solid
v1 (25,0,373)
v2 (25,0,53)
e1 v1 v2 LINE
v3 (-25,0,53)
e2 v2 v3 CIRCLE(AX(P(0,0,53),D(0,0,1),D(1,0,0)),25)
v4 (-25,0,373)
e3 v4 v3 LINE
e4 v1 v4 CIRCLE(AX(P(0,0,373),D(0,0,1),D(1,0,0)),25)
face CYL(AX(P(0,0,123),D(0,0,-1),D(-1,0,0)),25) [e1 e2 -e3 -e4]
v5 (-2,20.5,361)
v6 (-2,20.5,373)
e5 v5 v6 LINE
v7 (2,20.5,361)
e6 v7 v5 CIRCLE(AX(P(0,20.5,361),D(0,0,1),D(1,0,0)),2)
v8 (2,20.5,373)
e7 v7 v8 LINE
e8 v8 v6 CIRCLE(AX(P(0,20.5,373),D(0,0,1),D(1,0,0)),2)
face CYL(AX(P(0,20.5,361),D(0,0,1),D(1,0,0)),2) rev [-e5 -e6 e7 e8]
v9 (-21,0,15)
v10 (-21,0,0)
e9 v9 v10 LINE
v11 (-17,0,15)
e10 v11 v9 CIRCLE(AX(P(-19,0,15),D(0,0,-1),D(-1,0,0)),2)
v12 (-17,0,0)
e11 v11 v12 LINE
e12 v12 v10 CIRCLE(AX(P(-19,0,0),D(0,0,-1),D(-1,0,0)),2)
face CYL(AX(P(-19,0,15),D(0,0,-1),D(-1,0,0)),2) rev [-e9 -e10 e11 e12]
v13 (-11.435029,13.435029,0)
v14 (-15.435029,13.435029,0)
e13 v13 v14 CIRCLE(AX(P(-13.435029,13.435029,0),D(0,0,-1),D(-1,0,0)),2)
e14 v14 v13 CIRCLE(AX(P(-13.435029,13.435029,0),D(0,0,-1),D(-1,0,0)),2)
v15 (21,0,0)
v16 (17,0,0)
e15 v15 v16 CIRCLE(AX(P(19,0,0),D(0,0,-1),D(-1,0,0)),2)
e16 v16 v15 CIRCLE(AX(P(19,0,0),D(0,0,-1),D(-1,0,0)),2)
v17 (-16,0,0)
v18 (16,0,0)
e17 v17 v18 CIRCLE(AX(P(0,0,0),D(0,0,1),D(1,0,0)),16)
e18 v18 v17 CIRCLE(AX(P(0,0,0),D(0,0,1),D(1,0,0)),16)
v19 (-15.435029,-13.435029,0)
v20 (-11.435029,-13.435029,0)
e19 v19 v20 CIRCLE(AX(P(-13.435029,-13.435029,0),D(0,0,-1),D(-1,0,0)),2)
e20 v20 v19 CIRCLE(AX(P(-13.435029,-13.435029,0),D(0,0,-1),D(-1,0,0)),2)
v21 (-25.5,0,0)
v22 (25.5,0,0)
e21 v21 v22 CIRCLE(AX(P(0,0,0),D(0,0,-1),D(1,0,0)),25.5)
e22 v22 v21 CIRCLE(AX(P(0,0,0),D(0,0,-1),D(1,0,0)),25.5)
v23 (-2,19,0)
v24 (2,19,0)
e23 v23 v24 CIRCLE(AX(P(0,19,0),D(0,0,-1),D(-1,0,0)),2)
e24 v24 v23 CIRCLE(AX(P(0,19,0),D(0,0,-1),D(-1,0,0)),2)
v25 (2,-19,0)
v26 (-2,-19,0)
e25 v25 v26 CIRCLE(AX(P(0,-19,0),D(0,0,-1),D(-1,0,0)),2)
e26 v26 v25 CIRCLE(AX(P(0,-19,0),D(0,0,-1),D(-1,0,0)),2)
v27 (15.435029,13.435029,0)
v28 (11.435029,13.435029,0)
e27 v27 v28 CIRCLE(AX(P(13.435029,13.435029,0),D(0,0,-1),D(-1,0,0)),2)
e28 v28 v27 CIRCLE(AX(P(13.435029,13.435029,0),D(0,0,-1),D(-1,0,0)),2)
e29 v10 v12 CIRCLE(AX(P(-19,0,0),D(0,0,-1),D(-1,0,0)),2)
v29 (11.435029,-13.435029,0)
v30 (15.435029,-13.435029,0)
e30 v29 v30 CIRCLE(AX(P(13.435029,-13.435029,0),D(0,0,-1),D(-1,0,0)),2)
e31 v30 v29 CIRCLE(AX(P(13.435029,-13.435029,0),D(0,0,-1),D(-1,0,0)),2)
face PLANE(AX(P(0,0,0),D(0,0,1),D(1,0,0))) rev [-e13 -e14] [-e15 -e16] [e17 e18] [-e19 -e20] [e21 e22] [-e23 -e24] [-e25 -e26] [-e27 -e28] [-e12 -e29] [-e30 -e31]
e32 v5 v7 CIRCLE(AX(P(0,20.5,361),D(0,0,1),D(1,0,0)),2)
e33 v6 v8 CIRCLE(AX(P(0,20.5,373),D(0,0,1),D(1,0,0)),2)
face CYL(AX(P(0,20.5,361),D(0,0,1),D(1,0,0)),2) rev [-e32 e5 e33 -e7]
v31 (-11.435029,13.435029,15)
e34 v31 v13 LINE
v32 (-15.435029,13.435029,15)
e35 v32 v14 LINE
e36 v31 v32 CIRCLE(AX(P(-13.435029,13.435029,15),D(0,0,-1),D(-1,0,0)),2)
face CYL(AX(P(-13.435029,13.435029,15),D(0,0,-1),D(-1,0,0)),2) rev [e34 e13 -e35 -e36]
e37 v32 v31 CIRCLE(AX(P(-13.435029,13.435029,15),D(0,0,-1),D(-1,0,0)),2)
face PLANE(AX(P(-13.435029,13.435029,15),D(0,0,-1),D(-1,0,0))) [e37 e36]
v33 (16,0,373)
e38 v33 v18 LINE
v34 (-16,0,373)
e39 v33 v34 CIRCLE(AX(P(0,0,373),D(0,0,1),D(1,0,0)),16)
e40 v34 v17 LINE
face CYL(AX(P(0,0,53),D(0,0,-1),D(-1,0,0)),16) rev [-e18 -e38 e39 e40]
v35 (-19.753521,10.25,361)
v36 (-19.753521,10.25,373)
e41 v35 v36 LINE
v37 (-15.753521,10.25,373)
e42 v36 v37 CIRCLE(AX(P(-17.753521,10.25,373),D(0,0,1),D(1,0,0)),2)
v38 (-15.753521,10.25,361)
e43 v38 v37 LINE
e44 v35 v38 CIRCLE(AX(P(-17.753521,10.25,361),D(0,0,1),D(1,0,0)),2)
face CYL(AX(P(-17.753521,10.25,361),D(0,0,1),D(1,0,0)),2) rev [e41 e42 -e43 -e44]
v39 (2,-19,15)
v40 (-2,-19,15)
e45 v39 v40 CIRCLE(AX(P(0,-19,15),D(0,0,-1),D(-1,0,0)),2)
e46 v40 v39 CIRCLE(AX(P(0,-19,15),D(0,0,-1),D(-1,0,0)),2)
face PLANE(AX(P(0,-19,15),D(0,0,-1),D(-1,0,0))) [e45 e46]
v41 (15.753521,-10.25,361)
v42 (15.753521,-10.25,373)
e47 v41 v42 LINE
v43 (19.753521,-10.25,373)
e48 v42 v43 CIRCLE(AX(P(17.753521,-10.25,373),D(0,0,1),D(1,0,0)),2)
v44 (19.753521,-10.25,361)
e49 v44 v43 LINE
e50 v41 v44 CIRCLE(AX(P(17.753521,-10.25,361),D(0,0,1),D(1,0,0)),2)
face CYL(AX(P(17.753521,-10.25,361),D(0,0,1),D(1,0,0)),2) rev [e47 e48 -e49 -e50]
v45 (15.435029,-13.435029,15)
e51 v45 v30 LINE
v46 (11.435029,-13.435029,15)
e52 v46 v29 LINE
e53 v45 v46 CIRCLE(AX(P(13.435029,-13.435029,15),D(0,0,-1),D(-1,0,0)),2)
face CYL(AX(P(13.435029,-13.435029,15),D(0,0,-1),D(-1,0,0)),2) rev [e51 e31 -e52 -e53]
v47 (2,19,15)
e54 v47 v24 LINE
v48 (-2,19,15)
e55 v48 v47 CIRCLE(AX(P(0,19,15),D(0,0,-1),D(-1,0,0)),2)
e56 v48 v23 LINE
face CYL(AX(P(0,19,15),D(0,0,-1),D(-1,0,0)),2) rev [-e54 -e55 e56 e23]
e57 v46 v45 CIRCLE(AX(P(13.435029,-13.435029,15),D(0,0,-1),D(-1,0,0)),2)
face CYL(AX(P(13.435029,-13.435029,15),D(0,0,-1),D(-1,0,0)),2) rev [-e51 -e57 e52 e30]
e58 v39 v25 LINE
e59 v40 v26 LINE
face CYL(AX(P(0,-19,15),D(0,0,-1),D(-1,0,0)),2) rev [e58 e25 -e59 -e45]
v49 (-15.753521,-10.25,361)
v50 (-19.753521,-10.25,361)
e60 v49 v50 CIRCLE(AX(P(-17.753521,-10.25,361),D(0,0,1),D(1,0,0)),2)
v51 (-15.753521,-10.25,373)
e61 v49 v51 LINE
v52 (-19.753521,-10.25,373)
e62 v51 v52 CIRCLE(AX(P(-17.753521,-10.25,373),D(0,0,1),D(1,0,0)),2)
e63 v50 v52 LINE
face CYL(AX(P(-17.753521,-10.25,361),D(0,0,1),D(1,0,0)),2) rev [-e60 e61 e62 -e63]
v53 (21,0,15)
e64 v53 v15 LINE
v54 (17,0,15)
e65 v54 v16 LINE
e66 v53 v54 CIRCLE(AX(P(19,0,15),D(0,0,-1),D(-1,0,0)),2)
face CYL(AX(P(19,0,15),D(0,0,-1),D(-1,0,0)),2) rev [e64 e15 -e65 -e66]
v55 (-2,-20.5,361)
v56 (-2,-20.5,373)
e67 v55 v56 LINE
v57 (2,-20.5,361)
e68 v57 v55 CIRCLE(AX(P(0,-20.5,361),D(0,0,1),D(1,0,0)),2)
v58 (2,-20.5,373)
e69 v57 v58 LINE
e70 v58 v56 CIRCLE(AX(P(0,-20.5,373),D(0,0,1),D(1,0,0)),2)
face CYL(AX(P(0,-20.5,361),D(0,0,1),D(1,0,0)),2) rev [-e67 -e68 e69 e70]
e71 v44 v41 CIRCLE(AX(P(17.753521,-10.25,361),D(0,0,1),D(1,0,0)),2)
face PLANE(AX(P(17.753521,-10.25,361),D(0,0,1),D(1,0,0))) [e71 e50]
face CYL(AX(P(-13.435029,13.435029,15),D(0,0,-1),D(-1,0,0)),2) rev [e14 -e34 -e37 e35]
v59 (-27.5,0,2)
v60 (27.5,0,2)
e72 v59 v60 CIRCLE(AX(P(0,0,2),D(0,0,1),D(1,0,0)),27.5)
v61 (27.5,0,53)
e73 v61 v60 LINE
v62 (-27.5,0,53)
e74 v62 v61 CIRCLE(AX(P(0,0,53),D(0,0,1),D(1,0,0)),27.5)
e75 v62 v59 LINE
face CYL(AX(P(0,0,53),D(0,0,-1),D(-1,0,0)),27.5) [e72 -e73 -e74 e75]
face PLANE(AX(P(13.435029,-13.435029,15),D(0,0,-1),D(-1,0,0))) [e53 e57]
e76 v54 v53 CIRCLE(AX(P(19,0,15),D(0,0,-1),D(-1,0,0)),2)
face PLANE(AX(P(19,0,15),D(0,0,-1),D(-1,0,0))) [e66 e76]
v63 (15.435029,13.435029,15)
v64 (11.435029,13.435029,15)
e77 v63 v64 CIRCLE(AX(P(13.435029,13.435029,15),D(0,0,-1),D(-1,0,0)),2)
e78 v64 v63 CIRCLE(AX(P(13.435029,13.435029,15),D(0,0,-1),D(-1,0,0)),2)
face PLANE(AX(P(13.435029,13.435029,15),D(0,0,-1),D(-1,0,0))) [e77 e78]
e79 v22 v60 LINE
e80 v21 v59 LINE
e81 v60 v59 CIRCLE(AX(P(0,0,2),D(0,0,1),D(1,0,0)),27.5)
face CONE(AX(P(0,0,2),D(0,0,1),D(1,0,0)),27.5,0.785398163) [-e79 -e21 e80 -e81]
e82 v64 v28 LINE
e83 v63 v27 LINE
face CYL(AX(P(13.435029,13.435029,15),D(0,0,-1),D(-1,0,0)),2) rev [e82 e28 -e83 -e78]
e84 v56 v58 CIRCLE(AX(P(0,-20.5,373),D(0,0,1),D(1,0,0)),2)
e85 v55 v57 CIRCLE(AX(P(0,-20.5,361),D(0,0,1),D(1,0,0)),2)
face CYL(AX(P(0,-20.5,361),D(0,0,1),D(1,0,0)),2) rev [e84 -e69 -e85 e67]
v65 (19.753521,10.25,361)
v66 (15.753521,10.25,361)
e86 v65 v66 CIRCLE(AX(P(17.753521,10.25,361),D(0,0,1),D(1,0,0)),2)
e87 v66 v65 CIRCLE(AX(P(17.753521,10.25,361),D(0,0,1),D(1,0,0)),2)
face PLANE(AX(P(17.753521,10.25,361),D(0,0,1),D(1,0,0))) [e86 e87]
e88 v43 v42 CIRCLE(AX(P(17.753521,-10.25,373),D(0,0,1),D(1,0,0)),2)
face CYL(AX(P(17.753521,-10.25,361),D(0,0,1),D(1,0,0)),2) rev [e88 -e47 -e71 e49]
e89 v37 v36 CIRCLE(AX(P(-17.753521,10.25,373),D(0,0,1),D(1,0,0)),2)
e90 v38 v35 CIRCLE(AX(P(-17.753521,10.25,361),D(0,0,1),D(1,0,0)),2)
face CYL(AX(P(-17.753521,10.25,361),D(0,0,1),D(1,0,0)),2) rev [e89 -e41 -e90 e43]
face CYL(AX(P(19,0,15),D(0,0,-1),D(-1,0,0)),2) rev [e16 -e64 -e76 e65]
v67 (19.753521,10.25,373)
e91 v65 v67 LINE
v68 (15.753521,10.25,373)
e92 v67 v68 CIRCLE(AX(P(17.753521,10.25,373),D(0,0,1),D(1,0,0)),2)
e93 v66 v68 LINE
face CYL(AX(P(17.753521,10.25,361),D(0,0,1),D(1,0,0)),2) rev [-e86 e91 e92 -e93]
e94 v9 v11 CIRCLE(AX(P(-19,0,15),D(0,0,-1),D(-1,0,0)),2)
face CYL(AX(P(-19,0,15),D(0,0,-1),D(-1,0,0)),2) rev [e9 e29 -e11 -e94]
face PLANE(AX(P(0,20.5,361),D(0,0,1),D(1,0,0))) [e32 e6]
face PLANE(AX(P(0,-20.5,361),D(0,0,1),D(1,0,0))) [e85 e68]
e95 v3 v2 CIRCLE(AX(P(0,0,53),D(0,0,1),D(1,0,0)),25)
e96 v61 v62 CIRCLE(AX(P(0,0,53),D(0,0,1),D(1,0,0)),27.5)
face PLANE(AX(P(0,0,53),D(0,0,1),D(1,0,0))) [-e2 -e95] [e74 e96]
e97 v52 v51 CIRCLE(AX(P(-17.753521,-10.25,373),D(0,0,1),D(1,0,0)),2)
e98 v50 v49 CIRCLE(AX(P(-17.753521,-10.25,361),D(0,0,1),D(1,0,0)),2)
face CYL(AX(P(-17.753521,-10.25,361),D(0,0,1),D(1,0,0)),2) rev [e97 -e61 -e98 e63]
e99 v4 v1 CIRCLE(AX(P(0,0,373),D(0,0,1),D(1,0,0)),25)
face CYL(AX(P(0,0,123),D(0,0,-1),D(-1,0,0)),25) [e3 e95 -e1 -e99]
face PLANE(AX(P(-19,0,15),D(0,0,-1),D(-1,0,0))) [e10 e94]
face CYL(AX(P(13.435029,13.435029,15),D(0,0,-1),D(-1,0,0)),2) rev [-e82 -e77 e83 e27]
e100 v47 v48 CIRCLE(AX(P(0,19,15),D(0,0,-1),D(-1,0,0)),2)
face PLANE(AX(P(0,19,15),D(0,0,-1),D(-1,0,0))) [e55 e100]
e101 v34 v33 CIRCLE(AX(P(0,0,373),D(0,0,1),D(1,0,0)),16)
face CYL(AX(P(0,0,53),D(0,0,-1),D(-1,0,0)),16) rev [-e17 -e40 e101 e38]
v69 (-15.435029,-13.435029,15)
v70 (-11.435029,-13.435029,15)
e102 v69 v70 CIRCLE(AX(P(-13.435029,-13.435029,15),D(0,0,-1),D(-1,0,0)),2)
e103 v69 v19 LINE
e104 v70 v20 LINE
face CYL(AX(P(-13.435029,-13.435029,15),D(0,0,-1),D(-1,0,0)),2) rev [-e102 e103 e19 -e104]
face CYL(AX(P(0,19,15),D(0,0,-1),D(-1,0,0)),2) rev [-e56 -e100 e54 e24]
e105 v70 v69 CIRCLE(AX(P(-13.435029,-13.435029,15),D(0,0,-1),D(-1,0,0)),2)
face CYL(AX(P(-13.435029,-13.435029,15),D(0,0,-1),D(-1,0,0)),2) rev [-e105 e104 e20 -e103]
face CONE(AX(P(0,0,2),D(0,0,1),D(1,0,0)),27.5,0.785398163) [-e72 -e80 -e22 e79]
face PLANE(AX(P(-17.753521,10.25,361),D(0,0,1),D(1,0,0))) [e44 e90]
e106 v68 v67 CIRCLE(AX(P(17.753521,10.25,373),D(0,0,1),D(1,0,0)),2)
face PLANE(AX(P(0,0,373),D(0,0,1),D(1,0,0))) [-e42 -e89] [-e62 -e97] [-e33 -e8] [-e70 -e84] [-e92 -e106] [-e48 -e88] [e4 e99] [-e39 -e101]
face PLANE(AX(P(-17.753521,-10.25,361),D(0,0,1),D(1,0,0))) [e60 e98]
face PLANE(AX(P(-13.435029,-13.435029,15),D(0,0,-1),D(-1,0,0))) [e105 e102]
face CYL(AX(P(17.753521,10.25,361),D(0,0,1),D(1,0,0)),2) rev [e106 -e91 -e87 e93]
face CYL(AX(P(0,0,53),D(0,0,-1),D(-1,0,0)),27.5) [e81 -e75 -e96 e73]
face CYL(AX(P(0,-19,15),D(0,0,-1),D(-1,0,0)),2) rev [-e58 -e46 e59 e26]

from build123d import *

# Parameters (mm, degrees)
SKETCH1_R           = 27.5
SKETCH1_R_2         = 16
BOSS_EXTRUDE1_DEPTH = 53
SKETCH2_R           = 25
SKETCH2_R_2         = 16
BOSS_EXTRUDE2_DEPTH = 70
SKETCH3_R           = 2
CUT_EXTRUDE1_DEPTH  = 15
CHAMFER1_SIZE       = 2
SKETCH4_R           = 25
SKETCH4_R_2         = 16
BOSS_EXTRUDE3_DEPTH = 250
SKETCH5_R           = 2
CUT_EXTRUDE2_DEPTH  = 12


with BuildPart() as part:
    # Sketch1 → Boss-Extrude1 (new body)
    with BuildSketch(Plane.XY):
        Circle(SKETCH1_R)
        Circle(SKETCH1_R_2, mode=Mode.SUBTRACT)
    extrude(amount=BOSS_EXTRUDE1_DEPTH)

    # Sketch2 → Boss-Extrude2 (add)
    with BuildSketch(Plane.XY.offset(53)):
        Circle(SKETCH2_R)
        Circle(SKETCH2_R_2, mode=Mode.SUBTRACT)
    extrude(amount=BOSS_EXTRUDE2_DEPTH)

    # Sketch3 → Cut-Extrude1 (cut)
    with BuildSketch(Plane(origin=(0, 0, 0), x_dir=(-1, 0, 0), z_dir=(0, 0, -1))):
        with Locations((0, 19)):
            Circle(SKETCH3_R)
        with Locations((13.435028843, 13.435028843)):
            Circle(SKETCH3_R)
        with Locations((19, 0)):
            Circle(SKETCH3_R)
        with Locations((13.435028843, -13.435028843)):
            Circle(SKETCH3_R)
        with Locations((0, -19)):
            Circle(SKETCH3_R)
        with Locations((-13.435028843, -13.435028843)):
            Circle(SKETCH3_R)
        with Locations((-19, 0)):
            Circle(SKETCH3_R)
        with Locations((-13.435028843, 13.435028843)):
            Circle(SKETCH3_R)
    extrude(amount=-CUT_EXTRUDE1_DEPTH, mode=Mode.SUBTRACT)

    # Chamfer1
    chamfer1_edges = [part.edges().sort_by_distance(p)[0] for p in [
        (-27.5, 0, 0),
    ]]
    chamfer(chamfer1_edges, length=CHAMFER1_SIZE)

    # Sketch4 → Boss-Extrude3 (add)
    with BuildSketch(Plane.XY.offset(123)):
        Circle(SKETCH4_R)
        Circle(SKETCH4_R_2, mode=Mode.SUBTRACT)
    extrude(amount=BOSS_EXTRUDE3_DEPTH)

    # Sketch5 → Cut-Extrude2 (cut)
    with BuildSketch(Plane.XY.offset(373)):
        with Locations((0, 20.5)):
            Circle(SKETCH5_R)
        with Locations((17.753520778, 10.25)):
            Circle(SKETCH5_R)
        with Locations((17.753520778, -10.25)):
            Circle(SKETCH5_R)
        with Locations((0, -20.5)):
            Circle(SKETCH5_R)
        with Locations((-17.753520778, -10.25)):
            Circle(SKETCH5_R)
        with Locations((-17.753520778, 10.25)):
            Circle(SKETCH5_R)
    extrude(amount=-CUT_EXTRUDE2_DEPTH, mode=Mode.SUBTRACT)


solid = part.part
